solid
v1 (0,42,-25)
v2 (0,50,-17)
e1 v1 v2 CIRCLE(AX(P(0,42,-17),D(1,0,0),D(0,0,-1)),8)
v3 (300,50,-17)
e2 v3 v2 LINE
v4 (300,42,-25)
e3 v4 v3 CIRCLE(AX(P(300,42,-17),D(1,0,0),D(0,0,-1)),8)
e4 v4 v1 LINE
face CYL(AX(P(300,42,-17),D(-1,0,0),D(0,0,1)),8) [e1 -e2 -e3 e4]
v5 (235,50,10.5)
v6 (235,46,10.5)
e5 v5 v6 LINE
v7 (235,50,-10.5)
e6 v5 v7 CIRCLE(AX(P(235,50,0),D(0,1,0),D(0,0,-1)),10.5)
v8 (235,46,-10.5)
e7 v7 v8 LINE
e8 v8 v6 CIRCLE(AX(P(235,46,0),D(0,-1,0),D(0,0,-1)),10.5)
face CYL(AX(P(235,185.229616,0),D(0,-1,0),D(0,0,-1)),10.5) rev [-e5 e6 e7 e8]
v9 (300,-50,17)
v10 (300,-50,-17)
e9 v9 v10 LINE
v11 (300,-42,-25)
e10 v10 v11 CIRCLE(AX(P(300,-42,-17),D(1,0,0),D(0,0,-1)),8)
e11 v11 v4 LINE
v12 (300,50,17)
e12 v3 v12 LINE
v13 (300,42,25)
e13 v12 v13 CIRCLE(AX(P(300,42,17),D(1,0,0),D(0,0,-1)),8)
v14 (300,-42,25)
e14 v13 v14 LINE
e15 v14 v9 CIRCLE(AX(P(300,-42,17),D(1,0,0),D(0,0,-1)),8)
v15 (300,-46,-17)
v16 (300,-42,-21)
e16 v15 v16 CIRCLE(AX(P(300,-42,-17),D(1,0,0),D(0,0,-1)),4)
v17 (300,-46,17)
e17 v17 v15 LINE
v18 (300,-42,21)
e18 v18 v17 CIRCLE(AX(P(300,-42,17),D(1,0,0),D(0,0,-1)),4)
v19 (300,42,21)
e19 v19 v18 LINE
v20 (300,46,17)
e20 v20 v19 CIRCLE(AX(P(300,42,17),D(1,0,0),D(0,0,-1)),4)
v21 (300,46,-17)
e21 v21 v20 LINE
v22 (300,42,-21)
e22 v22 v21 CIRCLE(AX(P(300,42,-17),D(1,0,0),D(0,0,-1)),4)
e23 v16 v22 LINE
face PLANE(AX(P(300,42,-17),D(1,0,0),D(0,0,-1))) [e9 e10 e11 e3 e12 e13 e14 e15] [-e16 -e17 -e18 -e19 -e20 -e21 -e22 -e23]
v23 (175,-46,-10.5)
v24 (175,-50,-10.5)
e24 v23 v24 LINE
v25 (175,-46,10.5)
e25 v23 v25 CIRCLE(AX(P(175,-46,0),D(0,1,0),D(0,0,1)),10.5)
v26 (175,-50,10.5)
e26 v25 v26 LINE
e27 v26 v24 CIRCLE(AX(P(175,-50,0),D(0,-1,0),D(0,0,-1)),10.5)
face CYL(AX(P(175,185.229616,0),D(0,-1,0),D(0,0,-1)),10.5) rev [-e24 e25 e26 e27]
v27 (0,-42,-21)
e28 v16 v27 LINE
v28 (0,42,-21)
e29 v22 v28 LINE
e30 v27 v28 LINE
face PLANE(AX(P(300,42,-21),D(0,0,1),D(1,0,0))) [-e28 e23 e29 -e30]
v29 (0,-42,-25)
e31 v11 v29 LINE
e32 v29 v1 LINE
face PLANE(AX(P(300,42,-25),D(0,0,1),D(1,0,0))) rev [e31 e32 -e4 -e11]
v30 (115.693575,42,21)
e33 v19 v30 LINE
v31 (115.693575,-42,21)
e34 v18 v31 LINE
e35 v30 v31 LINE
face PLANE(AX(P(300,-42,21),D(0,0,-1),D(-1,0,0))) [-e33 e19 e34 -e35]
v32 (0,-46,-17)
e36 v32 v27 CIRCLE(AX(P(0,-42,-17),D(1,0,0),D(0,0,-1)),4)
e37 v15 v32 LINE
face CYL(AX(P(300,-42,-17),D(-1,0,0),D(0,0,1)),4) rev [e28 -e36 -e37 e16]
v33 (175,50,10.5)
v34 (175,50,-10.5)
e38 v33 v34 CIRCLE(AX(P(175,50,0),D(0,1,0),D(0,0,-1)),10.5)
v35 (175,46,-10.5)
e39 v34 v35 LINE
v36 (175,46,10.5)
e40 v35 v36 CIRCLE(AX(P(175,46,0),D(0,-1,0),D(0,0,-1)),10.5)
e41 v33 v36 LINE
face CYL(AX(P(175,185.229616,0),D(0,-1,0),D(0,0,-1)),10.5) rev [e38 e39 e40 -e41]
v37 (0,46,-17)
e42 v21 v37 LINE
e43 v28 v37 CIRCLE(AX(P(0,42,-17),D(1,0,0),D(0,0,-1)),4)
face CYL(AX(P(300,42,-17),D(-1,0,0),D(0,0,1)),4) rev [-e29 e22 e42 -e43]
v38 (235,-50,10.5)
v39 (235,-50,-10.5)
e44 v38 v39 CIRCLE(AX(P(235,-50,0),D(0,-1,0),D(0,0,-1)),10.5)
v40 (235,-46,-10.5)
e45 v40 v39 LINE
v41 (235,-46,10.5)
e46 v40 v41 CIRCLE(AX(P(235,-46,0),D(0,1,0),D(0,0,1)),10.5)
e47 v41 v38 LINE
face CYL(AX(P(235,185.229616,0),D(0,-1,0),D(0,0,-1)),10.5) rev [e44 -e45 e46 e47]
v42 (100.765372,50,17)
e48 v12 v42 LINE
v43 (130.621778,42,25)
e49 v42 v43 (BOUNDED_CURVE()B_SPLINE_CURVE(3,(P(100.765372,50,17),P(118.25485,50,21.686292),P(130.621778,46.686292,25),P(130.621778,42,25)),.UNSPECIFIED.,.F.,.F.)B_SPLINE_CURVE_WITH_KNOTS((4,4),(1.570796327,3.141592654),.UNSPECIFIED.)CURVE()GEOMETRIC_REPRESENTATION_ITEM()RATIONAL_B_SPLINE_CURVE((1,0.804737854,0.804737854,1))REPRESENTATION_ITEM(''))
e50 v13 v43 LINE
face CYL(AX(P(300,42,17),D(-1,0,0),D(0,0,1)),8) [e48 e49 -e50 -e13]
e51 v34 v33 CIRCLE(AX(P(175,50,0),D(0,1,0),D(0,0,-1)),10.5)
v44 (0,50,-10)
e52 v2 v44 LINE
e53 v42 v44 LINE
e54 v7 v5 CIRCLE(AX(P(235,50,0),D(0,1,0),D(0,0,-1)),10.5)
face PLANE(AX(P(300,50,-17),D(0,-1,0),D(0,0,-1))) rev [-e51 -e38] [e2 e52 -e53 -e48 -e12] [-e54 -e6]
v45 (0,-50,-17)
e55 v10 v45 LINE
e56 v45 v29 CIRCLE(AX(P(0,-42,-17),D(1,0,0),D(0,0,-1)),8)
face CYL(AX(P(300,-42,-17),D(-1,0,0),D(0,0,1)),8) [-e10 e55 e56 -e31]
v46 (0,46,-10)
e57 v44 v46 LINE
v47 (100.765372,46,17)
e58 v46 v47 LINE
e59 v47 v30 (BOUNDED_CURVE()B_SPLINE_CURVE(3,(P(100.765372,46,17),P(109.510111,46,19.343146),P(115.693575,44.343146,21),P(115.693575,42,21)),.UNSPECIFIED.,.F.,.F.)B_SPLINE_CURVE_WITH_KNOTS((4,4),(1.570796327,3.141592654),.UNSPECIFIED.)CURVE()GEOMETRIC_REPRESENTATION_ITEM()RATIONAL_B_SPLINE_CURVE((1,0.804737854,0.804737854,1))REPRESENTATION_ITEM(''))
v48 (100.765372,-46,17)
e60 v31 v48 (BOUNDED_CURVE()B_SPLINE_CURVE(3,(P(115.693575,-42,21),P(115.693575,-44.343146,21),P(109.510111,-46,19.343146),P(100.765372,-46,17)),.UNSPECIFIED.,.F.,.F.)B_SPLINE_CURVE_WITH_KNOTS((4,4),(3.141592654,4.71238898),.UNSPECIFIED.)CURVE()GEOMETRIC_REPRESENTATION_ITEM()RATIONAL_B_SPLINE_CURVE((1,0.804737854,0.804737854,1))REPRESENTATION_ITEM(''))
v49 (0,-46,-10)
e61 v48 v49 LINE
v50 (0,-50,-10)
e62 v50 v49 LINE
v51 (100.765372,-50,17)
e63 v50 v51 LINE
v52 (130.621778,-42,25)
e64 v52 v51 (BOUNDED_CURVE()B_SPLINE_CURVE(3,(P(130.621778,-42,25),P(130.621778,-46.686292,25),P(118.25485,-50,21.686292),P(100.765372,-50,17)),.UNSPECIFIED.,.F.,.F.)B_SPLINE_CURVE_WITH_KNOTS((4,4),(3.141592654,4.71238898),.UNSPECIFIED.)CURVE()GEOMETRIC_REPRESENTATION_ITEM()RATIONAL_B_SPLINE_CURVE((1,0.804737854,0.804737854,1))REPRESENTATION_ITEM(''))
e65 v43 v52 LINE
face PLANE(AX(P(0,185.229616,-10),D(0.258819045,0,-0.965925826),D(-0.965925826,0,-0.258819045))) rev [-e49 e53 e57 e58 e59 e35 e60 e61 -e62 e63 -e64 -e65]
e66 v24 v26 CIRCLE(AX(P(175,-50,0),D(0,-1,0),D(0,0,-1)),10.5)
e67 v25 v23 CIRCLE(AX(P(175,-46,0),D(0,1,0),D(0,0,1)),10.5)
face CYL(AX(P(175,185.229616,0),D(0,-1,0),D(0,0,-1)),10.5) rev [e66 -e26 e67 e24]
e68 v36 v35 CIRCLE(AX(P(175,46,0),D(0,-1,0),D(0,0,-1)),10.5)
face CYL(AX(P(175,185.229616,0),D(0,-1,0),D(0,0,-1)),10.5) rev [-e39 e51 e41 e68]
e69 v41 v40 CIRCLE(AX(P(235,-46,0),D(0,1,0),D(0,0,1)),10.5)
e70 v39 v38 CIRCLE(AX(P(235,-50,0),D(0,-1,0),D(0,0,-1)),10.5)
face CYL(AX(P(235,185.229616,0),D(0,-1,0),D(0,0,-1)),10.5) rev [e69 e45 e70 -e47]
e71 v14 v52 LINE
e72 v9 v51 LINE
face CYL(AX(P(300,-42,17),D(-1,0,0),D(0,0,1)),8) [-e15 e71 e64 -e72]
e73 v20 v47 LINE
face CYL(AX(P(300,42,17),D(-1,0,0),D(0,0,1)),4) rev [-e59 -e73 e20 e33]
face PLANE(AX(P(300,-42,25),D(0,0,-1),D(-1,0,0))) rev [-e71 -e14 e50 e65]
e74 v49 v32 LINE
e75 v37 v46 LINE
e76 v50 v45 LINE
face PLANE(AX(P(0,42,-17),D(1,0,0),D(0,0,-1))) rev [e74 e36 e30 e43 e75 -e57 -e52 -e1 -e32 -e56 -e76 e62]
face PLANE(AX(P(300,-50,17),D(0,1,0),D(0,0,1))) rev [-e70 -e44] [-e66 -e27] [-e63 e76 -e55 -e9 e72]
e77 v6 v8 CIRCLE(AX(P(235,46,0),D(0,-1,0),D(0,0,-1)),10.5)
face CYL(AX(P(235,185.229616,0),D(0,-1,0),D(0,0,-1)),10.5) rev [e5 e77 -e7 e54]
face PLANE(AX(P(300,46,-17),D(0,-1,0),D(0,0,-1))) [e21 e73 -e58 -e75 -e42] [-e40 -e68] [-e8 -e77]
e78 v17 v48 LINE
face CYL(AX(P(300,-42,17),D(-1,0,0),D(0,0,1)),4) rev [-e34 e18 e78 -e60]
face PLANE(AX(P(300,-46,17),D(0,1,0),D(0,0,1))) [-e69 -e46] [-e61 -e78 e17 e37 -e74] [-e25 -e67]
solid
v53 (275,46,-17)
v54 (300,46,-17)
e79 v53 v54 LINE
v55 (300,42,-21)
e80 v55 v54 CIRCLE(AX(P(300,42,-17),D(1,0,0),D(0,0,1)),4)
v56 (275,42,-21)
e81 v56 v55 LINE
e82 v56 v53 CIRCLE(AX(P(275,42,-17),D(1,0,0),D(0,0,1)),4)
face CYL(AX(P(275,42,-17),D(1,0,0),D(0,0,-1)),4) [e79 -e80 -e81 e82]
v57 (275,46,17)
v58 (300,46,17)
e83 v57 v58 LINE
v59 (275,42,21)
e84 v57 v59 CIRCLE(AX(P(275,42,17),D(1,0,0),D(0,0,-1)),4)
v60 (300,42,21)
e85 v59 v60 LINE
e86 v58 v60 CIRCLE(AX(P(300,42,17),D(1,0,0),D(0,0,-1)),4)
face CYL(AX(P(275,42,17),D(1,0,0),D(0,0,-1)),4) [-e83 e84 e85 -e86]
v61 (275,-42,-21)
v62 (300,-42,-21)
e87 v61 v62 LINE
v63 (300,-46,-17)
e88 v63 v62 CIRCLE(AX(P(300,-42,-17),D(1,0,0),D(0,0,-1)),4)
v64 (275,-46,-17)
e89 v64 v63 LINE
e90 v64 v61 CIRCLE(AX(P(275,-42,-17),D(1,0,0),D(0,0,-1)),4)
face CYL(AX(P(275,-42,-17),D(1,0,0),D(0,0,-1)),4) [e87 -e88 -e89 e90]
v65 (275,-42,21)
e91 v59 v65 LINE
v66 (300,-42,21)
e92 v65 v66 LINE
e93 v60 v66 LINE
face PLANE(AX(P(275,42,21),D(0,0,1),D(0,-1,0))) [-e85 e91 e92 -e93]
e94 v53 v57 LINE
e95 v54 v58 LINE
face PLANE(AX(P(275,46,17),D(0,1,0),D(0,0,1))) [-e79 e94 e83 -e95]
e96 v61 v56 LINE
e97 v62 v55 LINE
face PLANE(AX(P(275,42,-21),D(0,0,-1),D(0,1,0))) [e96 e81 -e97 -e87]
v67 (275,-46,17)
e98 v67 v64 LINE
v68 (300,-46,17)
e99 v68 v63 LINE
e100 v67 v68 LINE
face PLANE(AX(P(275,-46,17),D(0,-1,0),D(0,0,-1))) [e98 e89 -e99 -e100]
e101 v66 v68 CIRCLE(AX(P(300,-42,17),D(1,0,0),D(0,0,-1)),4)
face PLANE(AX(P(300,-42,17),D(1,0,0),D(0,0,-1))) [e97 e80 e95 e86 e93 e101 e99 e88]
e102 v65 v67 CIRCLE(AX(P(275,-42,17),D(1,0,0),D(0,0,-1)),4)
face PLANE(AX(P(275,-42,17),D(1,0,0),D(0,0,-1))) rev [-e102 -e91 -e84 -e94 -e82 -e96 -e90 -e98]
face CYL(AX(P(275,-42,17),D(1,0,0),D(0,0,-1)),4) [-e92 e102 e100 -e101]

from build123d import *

# Parameters (mm, degrees)
RECTANGULAR_TUBE_100_X_50_X_4_1_DEPTH = 300
CUT_EXTRUDE1_REACH                    = 319.214
SKETCH2_R                             = 10.5
BOSS_EXTRUDE1_DEPTH                   = 25


with BuildPart() as part:
    # Sketch1 → Rectangular tube 100 X 50 X 4 (1) (new body)
    with BuildSketch(Plane(origin=(0, 0, 0), x_dir=(0, 0, -1), z_dir=(1, 0, 0))):
        with BuildLine():
            Line((-17, -50), (17, -50))
            ThreePointArc((17, -50), (22.656854249, -47.656854249), (25, -42))
            Line((25, -42), (25, 42))
            ThreePointArc((25, 42), (22.656854249, 47.656854249), (17, 50))
            Line((17, 50), (-17, 50))
            ThreePointArc((-17, 50), (-22.656854249, 47.656854249), (-25, 42))
            Line((-25, 42), (-25, -42))
            ThreePointArc((-25, -42), (-22.656854249, -47.656854249), (-17, -50))
        make_face()
        with BuildLine():
            Line((-17, -46), (17, -46))
            ThreePointArc((17, -46), (19.828427125, -44.828427125), (21, -42))
            Line((21, -42), (21, 42))
            ThreePointArc((21, 42), (19.828427125, 44.828427125), (17, 46))
            Line((17, 46), (-17, 46))
            ThreePointArc((-17, 46), (-19.828427125, 44.828427125), (-21, 42))
            Line((-21, 42), (-21, -42))
            ThreePointArc((-21, -42), (-19.828427125, -44.828427125), (-17, -46))
        make_face(mode=Mode.SUBTRACT)
    extrude(amount=RECTANGULAR_TUBE_100_X_50_X_4_1_DEPTH)

    # Cut-Extrude1: up to this face of the body (flat: up to its plane)
    cut_extrude1_end = Plane(part.part.faces().sort_by_distance((150, 50, 0))[0])
    # Sketch2 → Cut-Extrude1 (cut, up to the picked face)
    with BuildSketch(Plane.XZ.offset(50), mode=Mode.PRIVATE) as cut_extrude1_sk1:
        with Locations(Location((235, 0, 0), (0, 0, 270))):
            Circle(SKETCH2_R)
    cut_extrude1_tool1 = split(extrude(cut_extrude1_sk1.sketch, amount=-CUT_EXTRUDE1_REACH, mode=Mode.PRIVATE), bisect_by=cut_extrude1_end, keep=Keep.BOTH, mode=Mode.PRIVATE)
    # Sketch2 → Cut-Extrude1 (cut, up to the picked face)
    with BuildSketch(Plane.XZ.offset(50), mode=Mode.PRIVATE) as cut_extrude1_sk2:
        with Locations(Location((175, 0, 0), (0, 0, 270))):
            Circle(SKETCH2_R)
    cut_extrude1_tool2 = split(extrude(cut_extrude1_sk2.sketch, amount=-CUT_EXTRUDE1_REACH, mode=Mode.PRIVATE), bisect_by=cut_extrude1_end, keep=Keep.BOTH, mode=Mode.PRIVATE)
    # Sketch2 → Cut-Extrude1 (cut, up to the picked face)
    with BuildSketch(Plane.XZ.offset(50), mode=Mode.PRIVATE) as cut_extrude1_sk3:
        Polygon((0, -10), (130.621778265, 25), (0, 25), align=None)
    cut_extrude1_tool3 = split(extrude(cut_extrude1_sk3.sketch, amount=-CUT_EXTRUDE1_REACH, mode=Mode.PRIVATE), bisect_by=cut_extrude1_end, keep=Keep.BOTH, mode=Mode.PRIVATE)
    add(cut_extrude1_tool1.solids().sort_by(Axis((235, -50, 0), (0, 1, 0)))[0], mode=Mode.SUBTRACT)
    add(cut_extrude1_tool2.solids().sort_by(Axis((175, -50, 0), (0, 1, 0)))[0], mode=Mode.SUBTRACT)
    add(cut_extrude1_tool3.solids().sort_by(Axis((43.540593, -50, 13.333333), (0, 1, 0)))[0], mode=Mode.SUBTRACT)


with BuildPart() as body_2:
    # Sketch3 → Boss-Extrude1 (new body)
    with BuildSketch(Plane(origin=(300, 0, 0), x_dir=(0, 0, -1), z_dir=(1, 0, 0))):
        with BuildLine():
            Line((-17, 46), (17, 46))
            ThreePointArc((17, 46), (19.828427125, 44.828427125), (21, 42))
            Line((21, 42), (21, -42))
            ThreePointArc((21, -42), (19.828427125, -44.828427125), (17, -46))
            Line((17, -46), (-17, -46))
            ThreePointArc((-17, -46), (-19.828427125, -44.828427125), (-21, -42))
            Line((-21, -42), (-21, 42))
            ThreePointArc((-21, 42), (-19.828427125, 44.828427125), (-17, 46))
        make_face()
    extrude(amount=-BOSS_EXTRUDE1_DEPTH)


solid = Compound([part.part, body_2.part])
